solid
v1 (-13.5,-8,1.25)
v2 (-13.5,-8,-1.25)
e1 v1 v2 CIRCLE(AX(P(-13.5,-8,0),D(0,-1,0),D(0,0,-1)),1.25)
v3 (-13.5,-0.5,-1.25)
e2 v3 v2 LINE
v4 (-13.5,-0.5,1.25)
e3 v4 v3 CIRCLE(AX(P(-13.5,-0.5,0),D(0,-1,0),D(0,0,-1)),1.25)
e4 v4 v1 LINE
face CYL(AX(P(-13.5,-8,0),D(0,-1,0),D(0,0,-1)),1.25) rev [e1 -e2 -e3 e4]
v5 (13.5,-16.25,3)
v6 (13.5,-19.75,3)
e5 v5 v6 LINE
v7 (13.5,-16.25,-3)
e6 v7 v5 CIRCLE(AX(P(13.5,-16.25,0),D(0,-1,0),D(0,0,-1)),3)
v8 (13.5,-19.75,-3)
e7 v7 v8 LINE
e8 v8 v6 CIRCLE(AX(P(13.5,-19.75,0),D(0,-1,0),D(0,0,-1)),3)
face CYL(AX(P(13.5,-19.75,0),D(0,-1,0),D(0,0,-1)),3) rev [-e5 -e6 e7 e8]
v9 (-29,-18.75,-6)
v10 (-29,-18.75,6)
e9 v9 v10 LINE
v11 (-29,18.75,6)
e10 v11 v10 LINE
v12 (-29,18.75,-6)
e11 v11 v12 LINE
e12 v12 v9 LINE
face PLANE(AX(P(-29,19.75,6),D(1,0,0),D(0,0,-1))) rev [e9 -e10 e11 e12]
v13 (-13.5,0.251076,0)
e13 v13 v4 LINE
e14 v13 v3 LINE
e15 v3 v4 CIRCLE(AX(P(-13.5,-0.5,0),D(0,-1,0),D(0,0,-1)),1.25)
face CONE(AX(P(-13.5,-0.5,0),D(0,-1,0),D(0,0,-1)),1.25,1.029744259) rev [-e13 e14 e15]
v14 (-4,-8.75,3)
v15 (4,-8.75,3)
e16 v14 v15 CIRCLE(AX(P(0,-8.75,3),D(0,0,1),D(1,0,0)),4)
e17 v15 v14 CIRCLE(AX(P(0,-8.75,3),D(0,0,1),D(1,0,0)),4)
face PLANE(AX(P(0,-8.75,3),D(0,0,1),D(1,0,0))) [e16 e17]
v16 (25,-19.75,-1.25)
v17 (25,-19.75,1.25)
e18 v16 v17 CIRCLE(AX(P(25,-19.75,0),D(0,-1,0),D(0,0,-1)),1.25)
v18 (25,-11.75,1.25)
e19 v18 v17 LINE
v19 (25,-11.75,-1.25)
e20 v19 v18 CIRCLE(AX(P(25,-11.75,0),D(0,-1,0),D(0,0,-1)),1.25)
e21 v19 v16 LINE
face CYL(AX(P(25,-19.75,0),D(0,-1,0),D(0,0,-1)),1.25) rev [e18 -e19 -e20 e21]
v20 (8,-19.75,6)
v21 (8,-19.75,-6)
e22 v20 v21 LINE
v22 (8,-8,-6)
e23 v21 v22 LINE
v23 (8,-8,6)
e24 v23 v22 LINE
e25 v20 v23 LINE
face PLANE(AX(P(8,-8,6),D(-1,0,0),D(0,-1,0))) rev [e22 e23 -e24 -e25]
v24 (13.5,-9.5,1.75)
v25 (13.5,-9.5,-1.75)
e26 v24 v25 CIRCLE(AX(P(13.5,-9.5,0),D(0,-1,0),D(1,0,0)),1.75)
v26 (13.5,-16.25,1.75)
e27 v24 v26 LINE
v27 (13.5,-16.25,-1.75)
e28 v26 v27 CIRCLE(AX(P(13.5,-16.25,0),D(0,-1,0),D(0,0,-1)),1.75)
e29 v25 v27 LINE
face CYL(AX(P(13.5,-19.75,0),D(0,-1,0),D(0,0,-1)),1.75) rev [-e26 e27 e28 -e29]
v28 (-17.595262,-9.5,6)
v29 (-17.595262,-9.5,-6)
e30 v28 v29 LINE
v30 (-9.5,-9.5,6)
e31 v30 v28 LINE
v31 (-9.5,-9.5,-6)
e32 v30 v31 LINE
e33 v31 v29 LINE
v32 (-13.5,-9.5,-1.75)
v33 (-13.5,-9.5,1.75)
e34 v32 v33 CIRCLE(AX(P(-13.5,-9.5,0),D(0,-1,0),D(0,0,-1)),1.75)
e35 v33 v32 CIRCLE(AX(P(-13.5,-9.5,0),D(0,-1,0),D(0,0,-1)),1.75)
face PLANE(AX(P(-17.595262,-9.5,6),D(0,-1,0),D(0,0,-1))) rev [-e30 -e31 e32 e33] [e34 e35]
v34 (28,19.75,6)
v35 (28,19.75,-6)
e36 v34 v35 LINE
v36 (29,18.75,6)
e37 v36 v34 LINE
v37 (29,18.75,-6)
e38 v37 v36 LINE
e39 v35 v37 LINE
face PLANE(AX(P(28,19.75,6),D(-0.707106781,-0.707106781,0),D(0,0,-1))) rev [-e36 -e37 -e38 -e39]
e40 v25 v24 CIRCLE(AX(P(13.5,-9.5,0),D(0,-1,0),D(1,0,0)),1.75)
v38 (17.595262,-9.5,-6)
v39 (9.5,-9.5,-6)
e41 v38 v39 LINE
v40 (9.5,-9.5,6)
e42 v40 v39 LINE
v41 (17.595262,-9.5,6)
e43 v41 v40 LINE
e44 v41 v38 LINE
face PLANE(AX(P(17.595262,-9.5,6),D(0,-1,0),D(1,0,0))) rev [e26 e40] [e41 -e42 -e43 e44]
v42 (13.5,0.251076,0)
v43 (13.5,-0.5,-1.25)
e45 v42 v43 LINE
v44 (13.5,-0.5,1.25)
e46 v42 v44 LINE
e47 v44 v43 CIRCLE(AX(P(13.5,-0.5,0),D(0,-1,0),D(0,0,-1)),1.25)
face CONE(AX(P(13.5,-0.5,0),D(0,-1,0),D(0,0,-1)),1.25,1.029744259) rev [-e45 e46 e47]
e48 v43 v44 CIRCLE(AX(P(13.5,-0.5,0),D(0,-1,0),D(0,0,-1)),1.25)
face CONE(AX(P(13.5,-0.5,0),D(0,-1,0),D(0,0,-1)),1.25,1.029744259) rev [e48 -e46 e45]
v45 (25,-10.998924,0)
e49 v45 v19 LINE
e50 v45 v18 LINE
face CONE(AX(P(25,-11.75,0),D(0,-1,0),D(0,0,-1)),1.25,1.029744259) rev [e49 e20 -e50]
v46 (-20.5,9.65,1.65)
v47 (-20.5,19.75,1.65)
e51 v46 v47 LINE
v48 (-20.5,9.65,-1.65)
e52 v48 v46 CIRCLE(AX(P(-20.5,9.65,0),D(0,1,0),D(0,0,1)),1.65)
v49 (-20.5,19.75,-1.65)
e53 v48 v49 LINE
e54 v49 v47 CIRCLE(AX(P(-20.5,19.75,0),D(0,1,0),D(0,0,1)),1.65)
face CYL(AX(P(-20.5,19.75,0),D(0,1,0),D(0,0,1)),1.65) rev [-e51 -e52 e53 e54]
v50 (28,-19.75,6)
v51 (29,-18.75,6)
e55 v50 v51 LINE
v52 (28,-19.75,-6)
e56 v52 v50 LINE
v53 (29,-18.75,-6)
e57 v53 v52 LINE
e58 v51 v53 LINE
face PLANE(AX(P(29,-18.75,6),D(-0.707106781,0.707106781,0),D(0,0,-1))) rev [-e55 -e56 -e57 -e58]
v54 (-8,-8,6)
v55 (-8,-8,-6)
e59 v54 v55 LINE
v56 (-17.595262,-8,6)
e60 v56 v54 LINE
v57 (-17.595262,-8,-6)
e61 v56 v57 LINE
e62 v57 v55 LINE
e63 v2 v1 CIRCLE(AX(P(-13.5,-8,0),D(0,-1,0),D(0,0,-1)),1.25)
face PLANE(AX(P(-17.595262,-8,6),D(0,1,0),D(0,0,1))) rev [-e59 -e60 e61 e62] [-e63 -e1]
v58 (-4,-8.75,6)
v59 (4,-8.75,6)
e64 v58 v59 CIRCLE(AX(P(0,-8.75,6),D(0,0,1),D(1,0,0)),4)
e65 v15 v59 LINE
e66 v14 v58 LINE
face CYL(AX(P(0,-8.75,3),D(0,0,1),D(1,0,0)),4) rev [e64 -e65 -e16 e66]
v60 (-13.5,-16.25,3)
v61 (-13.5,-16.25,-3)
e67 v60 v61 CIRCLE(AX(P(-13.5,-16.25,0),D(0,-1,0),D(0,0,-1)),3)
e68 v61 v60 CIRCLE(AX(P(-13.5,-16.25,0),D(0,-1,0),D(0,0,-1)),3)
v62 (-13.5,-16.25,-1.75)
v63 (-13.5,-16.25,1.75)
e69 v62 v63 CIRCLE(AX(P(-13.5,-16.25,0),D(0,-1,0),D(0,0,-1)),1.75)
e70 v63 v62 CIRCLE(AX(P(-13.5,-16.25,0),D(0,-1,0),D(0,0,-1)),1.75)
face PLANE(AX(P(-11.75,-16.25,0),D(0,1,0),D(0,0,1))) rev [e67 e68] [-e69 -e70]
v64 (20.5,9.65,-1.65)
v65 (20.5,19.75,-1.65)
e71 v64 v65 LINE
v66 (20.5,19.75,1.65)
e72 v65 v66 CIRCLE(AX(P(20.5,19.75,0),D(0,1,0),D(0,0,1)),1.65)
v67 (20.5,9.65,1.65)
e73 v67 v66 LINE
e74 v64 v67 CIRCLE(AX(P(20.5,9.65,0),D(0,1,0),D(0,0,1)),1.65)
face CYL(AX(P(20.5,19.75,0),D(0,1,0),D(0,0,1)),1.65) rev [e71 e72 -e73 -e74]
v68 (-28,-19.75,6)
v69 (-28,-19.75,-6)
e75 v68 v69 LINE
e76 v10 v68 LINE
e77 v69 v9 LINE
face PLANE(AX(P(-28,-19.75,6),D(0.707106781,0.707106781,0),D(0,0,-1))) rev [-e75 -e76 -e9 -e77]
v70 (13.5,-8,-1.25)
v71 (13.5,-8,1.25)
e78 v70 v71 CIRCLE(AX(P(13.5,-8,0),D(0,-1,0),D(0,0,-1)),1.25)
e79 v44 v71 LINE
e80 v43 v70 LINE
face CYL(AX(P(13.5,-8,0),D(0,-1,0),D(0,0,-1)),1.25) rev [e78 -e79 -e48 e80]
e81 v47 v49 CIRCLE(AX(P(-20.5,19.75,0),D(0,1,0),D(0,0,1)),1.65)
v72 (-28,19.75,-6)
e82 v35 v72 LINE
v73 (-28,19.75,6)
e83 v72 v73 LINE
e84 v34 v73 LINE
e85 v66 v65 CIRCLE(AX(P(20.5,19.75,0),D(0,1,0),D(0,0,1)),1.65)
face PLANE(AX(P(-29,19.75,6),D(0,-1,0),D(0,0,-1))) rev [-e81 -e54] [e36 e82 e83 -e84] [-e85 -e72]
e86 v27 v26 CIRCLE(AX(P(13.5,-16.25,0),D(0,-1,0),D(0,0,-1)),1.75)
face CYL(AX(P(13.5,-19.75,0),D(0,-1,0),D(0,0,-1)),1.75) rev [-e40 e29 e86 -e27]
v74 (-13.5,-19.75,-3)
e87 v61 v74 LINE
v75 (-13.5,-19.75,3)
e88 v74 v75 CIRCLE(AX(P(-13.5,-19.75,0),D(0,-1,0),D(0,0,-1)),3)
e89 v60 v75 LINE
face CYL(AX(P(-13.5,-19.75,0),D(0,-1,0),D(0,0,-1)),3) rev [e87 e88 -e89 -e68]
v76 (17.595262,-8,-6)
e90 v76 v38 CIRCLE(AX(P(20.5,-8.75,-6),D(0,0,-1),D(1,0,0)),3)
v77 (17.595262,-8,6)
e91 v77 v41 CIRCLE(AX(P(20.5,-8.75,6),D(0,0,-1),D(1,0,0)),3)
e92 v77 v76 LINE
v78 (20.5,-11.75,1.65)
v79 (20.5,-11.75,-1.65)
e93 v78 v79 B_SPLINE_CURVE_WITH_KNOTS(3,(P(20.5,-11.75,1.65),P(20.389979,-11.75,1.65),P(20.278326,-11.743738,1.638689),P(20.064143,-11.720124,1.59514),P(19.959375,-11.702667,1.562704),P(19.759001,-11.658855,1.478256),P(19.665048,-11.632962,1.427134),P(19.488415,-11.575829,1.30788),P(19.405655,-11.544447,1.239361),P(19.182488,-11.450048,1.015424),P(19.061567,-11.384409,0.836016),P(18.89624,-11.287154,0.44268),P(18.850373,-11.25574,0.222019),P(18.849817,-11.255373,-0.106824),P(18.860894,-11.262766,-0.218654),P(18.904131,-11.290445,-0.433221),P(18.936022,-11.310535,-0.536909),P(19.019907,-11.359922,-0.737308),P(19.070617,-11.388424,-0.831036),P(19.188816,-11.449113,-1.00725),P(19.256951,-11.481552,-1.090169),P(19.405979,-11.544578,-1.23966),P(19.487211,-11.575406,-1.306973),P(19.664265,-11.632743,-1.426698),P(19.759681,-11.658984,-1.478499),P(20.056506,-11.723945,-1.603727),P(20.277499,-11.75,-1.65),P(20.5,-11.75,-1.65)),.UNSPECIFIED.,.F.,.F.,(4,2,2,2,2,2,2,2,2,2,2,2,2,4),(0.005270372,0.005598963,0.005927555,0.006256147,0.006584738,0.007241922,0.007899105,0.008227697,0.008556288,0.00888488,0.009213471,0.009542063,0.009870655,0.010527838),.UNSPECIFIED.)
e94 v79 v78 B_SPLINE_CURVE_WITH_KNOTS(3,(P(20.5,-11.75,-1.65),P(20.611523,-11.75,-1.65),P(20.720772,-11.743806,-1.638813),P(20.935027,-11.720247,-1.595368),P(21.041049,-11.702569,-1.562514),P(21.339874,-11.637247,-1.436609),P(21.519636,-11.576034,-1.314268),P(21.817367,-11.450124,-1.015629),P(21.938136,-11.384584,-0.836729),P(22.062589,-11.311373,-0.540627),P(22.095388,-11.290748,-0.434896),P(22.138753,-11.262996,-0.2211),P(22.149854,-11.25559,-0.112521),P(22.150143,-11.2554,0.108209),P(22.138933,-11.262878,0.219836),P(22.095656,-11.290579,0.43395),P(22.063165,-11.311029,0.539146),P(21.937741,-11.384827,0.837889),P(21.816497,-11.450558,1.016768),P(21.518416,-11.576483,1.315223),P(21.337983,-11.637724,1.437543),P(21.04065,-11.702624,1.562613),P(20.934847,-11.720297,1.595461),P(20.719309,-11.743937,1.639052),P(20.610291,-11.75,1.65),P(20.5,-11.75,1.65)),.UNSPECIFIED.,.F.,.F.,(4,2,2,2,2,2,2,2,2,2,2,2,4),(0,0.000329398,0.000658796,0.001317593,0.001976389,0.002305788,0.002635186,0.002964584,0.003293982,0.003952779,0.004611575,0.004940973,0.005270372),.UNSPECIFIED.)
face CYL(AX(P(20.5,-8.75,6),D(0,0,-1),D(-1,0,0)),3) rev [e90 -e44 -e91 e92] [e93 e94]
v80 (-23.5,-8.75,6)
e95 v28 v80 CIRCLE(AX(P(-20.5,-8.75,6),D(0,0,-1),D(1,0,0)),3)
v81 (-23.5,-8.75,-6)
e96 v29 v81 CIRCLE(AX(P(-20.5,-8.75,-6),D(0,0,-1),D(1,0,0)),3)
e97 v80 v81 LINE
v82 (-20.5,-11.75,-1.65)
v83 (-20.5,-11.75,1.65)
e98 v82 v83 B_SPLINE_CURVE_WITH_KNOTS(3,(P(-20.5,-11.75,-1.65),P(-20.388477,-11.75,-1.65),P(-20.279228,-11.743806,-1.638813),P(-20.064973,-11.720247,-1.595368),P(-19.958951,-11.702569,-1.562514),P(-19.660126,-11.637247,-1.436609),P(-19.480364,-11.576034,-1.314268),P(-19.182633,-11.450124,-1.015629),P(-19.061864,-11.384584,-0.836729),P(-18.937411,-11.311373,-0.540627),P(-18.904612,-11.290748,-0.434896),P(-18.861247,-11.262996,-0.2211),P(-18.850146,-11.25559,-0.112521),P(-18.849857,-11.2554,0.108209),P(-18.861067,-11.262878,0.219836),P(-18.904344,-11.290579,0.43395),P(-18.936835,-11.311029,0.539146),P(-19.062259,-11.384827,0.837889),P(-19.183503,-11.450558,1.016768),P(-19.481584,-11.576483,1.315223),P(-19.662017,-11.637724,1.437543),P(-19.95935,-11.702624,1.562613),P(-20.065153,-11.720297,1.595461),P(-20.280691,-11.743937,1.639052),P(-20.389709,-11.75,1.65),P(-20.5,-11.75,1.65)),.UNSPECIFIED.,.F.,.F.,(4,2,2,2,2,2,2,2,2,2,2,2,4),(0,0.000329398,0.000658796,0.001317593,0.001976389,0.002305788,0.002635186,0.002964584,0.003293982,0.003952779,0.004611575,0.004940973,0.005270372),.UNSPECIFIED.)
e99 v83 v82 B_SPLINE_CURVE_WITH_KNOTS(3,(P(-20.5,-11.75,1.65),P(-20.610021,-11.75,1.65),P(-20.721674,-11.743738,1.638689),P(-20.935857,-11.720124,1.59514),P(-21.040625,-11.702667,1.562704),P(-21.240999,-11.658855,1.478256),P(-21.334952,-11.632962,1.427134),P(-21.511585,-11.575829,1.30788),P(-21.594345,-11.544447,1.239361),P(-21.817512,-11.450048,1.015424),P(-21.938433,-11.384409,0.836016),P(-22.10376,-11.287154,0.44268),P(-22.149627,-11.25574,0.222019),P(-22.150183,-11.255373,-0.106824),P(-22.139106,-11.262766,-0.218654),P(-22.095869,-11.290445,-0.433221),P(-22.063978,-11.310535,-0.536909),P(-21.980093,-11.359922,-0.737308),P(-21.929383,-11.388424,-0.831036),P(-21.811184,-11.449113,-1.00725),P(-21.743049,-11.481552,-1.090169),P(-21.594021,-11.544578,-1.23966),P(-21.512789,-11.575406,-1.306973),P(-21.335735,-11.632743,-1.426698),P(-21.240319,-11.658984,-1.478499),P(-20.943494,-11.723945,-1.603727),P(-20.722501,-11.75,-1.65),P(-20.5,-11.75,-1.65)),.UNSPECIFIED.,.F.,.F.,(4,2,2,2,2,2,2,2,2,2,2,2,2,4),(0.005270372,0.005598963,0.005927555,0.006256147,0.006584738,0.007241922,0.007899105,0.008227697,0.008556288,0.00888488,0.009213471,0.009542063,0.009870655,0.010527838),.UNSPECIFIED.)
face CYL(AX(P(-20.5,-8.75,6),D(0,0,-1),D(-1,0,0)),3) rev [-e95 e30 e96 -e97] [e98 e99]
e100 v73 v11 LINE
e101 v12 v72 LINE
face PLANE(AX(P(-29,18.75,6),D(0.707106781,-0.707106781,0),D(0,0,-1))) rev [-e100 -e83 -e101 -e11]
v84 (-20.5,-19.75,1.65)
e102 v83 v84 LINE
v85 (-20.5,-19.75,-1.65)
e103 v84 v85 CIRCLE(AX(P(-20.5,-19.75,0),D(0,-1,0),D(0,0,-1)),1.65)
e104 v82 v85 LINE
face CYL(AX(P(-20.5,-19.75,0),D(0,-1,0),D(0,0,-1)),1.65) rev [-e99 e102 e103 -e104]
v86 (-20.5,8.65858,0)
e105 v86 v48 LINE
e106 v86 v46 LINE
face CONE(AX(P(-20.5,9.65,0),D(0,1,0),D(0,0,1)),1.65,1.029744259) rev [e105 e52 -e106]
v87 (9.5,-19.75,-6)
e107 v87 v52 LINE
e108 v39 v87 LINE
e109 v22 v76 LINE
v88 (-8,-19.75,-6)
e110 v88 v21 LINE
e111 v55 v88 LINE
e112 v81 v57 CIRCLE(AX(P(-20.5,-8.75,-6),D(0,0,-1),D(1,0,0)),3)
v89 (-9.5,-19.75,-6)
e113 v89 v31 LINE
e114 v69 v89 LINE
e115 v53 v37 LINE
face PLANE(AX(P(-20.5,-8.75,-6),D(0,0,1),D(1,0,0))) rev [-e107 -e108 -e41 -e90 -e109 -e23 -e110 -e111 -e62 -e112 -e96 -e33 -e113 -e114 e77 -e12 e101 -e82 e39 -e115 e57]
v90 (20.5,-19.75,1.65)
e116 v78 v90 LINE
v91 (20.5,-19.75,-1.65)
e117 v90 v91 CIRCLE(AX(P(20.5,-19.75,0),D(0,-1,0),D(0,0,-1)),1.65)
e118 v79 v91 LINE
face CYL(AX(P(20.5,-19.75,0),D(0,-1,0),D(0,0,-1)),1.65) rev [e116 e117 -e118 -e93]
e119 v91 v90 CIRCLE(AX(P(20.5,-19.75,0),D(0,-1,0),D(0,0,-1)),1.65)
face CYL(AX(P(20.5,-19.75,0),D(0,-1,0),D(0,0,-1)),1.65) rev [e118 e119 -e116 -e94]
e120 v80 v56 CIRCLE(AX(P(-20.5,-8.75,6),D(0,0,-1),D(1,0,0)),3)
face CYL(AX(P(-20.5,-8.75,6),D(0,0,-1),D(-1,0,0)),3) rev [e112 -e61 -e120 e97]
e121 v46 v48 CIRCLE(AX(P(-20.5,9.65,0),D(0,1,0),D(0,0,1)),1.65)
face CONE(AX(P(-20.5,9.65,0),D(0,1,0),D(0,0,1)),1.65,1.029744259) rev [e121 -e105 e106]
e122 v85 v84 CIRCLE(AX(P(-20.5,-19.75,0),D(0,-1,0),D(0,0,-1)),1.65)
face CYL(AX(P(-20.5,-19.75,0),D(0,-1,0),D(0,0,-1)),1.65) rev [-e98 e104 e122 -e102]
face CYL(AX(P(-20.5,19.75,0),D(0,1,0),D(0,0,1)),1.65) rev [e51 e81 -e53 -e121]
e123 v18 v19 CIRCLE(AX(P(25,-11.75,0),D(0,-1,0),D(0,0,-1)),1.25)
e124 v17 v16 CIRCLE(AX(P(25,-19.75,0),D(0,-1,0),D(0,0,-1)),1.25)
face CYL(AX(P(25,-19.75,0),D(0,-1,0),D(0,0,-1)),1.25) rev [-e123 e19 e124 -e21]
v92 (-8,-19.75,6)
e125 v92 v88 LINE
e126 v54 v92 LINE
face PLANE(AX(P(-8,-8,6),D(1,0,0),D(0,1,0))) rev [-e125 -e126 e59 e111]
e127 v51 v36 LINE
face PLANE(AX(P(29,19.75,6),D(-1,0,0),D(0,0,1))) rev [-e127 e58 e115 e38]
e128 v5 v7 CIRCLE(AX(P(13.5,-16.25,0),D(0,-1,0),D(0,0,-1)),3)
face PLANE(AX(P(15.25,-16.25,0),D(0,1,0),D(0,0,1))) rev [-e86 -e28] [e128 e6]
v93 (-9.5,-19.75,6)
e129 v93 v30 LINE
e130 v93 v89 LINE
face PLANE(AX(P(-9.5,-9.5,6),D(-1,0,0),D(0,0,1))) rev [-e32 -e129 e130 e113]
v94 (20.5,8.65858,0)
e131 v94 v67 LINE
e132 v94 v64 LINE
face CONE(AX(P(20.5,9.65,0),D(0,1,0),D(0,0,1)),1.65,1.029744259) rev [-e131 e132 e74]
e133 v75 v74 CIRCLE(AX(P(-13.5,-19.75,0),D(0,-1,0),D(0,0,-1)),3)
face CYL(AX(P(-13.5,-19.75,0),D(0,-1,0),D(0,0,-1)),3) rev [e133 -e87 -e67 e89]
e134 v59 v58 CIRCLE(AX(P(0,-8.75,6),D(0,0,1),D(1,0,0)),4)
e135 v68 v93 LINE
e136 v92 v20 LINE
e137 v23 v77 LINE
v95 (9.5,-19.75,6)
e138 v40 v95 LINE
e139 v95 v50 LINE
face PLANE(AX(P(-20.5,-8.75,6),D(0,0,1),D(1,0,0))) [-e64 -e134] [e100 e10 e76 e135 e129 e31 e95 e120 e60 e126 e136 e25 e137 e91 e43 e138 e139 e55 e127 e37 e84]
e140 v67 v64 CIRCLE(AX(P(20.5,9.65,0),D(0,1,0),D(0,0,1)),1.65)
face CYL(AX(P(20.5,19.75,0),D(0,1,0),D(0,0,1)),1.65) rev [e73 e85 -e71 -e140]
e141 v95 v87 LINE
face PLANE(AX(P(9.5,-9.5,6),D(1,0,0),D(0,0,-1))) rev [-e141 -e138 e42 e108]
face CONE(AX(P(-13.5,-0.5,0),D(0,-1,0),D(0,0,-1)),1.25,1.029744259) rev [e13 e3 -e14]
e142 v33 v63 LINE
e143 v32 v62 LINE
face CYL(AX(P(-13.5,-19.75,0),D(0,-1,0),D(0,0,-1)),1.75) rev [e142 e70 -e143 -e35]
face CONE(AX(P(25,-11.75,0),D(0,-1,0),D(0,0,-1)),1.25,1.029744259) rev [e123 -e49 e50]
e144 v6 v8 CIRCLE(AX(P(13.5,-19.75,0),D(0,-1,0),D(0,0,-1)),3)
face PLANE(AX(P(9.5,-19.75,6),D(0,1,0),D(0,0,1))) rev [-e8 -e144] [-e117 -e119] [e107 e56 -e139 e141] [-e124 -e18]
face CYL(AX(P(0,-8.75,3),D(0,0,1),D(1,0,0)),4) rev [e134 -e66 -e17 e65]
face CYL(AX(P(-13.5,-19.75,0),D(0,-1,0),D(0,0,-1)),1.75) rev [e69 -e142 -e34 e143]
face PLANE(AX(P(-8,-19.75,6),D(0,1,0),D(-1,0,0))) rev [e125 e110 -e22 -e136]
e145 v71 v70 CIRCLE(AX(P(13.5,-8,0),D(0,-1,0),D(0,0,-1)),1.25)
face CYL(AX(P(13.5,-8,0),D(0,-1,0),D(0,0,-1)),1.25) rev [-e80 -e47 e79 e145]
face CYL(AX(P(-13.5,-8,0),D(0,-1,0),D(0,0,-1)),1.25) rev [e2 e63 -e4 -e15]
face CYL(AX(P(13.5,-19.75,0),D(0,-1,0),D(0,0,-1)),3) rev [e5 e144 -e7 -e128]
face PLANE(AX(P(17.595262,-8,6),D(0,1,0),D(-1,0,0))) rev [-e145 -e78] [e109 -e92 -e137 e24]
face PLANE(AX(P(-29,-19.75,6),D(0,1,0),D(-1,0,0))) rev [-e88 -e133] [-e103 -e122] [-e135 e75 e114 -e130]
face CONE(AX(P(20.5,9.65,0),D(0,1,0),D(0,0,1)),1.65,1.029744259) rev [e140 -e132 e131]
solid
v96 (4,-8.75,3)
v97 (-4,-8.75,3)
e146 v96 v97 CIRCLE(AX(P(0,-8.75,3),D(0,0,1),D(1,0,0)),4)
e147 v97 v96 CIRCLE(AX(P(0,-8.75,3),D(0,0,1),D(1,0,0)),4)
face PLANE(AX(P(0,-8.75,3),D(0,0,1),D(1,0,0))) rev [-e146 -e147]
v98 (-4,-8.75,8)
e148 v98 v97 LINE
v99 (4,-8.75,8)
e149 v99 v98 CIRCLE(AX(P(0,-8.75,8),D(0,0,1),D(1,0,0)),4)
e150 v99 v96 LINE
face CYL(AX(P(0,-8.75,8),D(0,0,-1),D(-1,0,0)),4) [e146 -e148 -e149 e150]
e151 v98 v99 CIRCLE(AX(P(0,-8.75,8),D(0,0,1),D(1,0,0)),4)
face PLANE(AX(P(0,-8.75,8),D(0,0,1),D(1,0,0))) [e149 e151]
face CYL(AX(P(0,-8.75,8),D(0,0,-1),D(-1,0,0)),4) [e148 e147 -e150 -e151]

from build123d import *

# Parameters (mm, degrees)
BOSS_EXTRUDE1_DEPTH                     = 6
M4_TAPPED_HOLE1_AT_2_COUNT              = 2
M4_TAPPED_HOLE1_AT_2_PITCH              = 41
CBORE_FOR_M3_HEX_HEAD_BOLT1_D           = 3.5
CBORE_FOR_M3_HEX_HEAD_BOLT1_DEPTH       = 10.25
CBORE_FOR_M3_HEX_HEAD_BOLT1_CBORE_D     = 6
CBORE_FOR_M3_HEX_HEAD_BOLT1_CBORE_DEPTH = 3.5
M3_TAPPED_HOLE1_D                       = 2.5
M3_TAPPED_HOLE1_DEPTH                   = 7.5
M3_TAPPED_HOLE1_TIP                     = 0.751075774
M3_TAPPED_HOLE2_D                       = 2.5
M3_TAPPED_HOLE2_DEPTH                   = 8
M3_TAPPED_HOLE2_TIP                     = 0.751075774
SKETCH10_R                              = 4
CUT_EXTRUDE1_DEPTH                      = 3
SKETCH11_R                              = 4
BOSS_EXTRUDE2_DEPTH                     = 5
CHAMFER1_SIZE                           = 1


with BuildPart() as part:
    # Sketch1 → Boss-Extrude1 (new, symmetric)
    with BuildSketch(Plane.XY):
        with BuildLine():
            Line((-29, 19.75), (29, 19.75))
            Line((29, 19.75), (29, -19.75))
            Line((29, -19.75), (9.5, -19.75))
            Line((9.5, -19.75), (9.5, -9.5))
            Line((9.5, -9.5), (17.59526249, -9.5))
            ThreePointArc((17.59526249, -9.5), (23.5, -8.75), (17.59526249, -8))
            Line((17.59526249, -8), (8, -8))
            Line((8, -8), (8, -19.75))
            Line((8, -19.75), (-8, -19.75))
            Line((-8, -19.75), (-8, -8))
            Line((-8, -8), (-17.59526249, -8))
            ThreePointArc((-17.59526249, -8), (-23.5, -8.75), (-17.59526249, -9.5))
            Line((-17.59526249, -9.5), (-9.5, -9.5))
            Line((-9.5, -9.5), (-9.5, -19.75))
            Line((-9.5, -19.75), (-29, -19.75))
            Line((-29, -19.75), (-29, 19.75))
        make_face()
    extrude(amount=BOSS_EXTRUDE1_DEPTH, both=True)

    # Sketch2 → M4 Tapped Hole1 (revolve, cut)
    with BuildSketch(Plane(origin=(-20.5, 19.75, 0), x_dir=(0, 0, 1), z_dir=(1, 0, 0))):
        Polygon((0, 0), (0, 11.091420021), (1.65, 10.1), (1.65, 0), align=None)
    m4_tapped_hole1 = revolve(axis=Axis((-20.5, 26.1, 0), (0, -1, 0)), mode=Mode.SUBTRACT)

    # M4 Tapped Hole1 at 2: M4 Tapped Hole1 ×2
    with Locations(*[(i * M4_TAPPED_HOLE1_AT_2_PITCH, 0, 0) for i in range(1, M4_TAPPED_HOLE1_AT_2_COUNT)]):
        add(m4_tapped_hole1, mode=Mode.SUBTRACT)

    # Mirror1: M4 Tapped Hole1 across plane
    add(m4_tapped_hole1.mirror(Plane.ZX), mode=Mode.SUBTRACT)

    # Mirror1 copy 1 sketch → Mirror1 copy 1 (revolve, cut)
    with BuildSketch(Plane(origin=(20.5, -19.75, 0), x_dir=(0, 0, 1), z_dir=(1, 0, 0))):
        Polygon((0, 0), (0, -11.091420021), (1.65, -10.1), (1.65, 0), align=None)
    revolve(axis=Axis((20.5, -26.1, 0), (0, -1, 0)), mode=Mode.SUBTRACT)

    # CBORE for M3 Hex Head Bolt1
    with Locations(Plane.XZ.offset(19.75)):
        with Locations((-13.5, 0), (13.5, 0)):
            CounterBoreHole(CBORE_FOR_M3_HEX_HEAD_BOLT1_D / 2, CBORE_FOR_M3_HEX_HEAD_BOLT1_CBORE_D / 2, CBORE_FOR_M3_HEX_HEAD_BOLT1_CBORE_DEPTH, depth=CBORE_FOR_M3_HEX_HEAD_BOLT1_DEPTH)

    # M3 Tapped Hole1
    with Locations(Plane.XZ.offset(8)):
        with Locations((-13.5, 0), (13.5, 0)):
            Hole(M3_TAPPED_HOLE1_D / 2, depth=M3_TAPPED_HOLE1_DEPTH)
            with Locations((0, 0, -(M3_TAPPED_HOLE1_DEPTH + M3_TAPPED_HOLE1_TIP / 2))):  # 118° drill point
                Cone(0, M3_TAPPED_HOLE1_D / 2, M3_TAPPED_HOLE1_TIP, mode=Mode.SUBTRACT)

    # M3 Tapped Hole2
    with Locations(Plane.XZ.offset(19.75)):
        with Locations((25, 0)):
            Hole(M3_TAPPED_HOLE2_D / 2, depth=M3_TAPPED_HOLE2_DEPTH)
            with Locations((0, 0, -(M3_TAPPED_HOLE2_DEPTH + M3_TAPPED_HOLE2_TIP / 2))):  # 118° drill point
                Cone(0, M3_TAPPED_HOLE2_D / 2, M3_TAPPED_HOLE2_TIP, mode=Mode.SUBTRACT)

    # Sketch10 → Cut-Extrude1 (cut)
    with BuildSketch(Plane.XY.offset(6)):
        with Locations((0, -8.75)):
            Circle(SKETCH10_R)
    extrude(amount=-CUT_EXTRUDE1_DEPTH, mode=Mode.SUBTRACT)

    # Chamfer1
    chamfer1_edges = [part.edges().sort_by_distance(p)[0] for p in [
        (-29, -19.75, 0),
        (-29, 19.75, 0),
        (29, 19.75, 0),
        (29, -19.75, 0),
    ]]
    chamfer(chamfer1_edges, length=CHAMFER1_SIZE)


with BuildPart() as body_2:
    # Sketch11 → Boss-Extrude2 (new body)
    with BuildSketch(Plane.XY.offset(3)):
        with Locations((0, -8.75)):
            Circle(SKETCH11_R)
    extrude(amount=BOSS_EXTRUDE2_DEPTH)


solid = Compound([part.part, body_2.part])
